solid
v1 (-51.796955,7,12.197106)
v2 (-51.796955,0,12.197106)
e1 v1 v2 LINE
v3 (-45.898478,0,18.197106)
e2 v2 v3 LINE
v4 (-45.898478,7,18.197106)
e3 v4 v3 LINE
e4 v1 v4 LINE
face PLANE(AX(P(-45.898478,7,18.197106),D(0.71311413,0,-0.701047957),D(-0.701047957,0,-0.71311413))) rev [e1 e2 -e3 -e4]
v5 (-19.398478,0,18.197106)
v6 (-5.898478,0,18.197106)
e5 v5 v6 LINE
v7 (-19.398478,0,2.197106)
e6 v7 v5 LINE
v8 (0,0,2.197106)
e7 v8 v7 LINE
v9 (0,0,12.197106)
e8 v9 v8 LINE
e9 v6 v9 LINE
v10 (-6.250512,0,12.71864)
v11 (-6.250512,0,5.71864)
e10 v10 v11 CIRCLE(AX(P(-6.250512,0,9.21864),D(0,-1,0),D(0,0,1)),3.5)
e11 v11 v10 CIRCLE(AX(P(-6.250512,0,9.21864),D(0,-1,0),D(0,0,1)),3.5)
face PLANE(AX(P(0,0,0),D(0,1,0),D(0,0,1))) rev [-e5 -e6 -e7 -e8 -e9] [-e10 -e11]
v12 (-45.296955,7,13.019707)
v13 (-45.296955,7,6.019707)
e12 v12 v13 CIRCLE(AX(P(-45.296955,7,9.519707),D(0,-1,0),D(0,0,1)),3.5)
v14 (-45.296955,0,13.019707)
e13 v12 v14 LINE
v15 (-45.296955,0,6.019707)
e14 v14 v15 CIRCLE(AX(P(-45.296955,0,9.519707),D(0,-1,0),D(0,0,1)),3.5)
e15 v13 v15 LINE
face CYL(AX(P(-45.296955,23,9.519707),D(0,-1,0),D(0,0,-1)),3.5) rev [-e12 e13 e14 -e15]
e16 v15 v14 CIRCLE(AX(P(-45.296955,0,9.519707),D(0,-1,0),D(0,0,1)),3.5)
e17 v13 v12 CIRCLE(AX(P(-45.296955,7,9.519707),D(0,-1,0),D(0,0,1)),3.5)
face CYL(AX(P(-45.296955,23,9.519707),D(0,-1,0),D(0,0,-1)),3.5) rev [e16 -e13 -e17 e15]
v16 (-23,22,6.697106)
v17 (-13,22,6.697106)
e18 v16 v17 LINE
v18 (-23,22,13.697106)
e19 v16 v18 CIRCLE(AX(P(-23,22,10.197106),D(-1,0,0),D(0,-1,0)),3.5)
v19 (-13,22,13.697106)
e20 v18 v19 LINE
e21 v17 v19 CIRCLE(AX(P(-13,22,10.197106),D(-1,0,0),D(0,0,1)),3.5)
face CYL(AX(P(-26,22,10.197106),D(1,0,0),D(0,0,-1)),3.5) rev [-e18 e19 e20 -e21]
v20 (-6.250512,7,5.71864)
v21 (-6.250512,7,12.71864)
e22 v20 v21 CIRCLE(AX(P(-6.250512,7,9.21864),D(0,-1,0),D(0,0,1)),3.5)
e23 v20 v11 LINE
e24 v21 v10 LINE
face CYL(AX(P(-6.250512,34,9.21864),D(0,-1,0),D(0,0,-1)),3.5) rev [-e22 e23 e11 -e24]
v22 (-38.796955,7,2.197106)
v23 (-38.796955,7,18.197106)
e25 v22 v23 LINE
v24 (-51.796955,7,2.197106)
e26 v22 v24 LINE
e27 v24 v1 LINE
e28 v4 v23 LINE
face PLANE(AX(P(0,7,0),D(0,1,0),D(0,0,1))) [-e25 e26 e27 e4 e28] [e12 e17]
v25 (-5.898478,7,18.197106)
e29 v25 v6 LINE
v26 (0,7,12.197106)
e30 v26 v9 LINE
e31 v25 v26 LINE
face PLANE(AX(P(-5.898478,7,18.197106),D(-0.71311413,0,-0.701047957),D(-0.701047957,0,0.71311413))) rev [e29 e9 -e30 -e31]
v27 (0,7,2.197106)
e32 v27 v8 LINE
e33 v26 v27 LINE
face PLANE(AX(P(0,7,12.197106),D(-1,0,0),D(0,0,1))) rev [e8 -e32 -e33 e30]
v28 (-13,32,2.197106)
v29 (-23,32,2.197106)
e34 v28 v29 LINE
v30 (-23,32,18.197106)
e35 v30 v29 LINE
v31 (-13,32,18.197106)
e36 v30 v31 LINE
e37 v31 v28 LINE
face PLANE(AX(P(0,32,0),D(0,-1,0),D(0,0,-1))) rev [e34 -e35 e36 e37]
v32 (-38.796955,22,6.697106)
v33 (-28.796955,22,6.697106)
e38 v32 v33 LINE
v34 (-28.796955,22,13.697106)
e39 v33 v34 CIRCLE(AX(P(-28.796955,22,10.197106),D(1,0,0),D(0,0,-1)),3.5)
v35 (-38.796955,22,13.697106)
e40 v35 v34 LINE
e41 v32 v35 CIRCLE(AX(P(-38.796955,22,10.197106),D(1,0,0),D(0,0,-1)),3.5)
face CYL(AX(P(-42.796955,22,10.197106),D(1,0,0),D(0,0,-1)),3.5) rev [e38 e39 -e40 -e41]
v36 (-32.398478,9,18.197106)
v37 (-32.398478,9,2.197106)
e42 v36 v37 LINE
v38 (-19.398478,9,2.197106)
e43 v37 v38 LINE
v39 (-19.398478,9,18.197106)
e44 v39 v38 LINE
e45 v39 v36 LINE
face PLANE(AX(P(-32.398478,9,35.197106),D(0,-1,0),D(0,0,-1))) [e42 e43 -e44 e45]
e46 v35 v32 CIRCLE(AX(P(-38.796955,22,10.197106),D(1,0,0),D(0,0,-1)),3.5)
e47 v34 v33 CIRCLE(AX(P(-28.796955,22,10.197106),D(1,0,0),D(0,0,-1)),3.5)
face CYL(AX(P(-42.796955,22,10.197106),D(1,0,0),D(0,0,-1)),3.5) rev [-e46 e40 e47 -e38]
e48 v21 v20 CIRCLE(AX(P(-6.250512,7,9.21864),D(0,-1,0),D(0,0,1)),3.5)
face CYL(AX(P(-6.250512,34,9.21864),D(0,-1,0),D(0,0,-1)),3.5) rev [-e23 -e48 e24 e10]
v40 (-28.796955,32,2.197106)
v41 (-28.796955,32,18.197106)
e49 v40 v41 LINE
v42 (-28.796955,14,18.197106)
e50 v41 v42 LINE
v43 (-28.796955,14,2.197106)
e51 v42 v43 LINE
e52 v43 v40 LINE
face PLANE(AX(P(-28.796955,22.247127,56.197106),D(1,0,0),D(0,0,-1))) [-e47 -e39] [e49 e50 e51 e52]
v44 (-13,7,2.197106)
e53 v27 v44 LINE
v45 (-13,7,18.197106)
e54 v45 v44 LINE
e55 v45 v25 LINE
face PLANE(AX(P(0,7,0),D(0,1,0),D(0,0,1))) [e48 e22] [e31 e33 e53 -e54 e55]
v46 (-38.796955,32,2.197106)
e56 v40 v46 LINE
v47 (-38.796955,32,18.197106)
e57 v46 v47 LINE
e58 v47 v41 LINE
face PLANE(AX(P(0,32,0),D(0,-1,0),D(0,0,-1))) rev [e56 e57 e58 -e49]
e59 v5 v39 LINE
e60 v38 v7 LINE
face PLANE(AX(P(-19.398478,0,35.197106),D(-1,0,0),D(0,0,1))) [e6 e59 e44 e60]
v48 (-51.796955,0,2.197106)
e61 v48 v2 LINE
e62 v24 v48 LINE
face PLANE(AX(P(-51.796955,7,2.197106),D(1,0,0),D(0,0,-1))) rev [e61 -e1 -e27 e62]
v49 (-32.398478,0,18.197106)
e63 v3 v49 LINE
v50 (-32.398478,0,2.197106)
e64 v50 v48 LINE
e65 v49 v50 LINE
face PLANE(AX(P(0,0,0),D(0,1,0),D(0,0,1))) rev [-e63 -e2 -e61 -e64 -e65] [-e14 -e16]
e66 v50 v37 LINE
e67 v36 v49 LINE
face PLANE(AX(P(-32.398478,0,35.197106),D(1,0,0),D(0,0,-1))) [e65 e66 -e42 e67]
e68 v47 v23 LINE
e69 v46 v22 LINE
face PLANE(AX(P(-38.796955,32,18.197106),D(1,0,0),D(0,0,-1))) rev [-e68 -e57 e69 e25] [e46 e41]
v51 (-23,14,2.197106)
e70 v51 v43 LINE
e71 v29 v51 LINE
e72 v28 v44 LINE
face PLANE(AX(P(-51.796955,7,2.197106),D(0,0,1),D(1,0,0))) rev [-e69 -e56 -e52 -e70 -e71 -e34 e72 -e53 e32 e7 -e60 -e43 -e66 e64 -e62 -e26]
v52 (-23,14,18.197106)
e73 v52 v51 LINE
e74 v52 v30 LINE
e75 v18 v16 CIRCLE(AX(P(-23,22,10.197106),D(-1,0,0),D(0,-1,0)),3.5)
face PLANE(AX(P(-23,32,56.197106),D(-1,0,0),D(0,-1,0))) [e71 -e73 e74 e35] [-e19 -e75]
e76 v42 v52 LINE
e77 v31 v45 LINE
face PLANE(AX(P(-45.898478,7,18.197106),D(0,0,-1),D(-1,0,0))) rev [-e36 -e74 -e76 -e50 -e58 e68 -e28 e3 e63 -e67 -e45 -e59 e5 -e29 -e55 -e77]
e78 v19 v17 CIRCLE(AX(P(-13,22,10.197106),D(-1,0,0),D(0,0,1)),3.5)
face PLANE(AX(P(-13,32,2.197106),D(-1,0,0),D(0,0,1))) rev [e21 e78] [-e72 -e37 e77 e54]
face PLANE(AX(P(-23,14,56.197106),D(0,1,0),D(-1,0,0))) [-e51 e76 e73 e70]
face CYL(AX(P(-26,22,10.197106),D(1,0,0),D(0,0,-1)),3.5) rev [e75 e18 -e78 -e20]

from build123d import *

# Parameters (mm, degrees)
BASE_PLATE_DEPTH              = 7
BASE_RELIEF_CUT_DEPTH         = 16
BASE_RELIEF_CUT_DEPTH_BACK    = 18
BASE_RELIEF_CUT_SKETCH_R      = 3.5
BASE_TRIM_CUT_DEPTH           = 27
BASE_TRIM_CUT_DEPTH_BACK      = 35
BASE_TRIM_CUT_SKETCH_R        = 3.5
UPRIGHT_BLOCK_SKETCH_13X13_W  = 25.796955258
UPRIGHT_BLOCK_SKETCH_13X13_H  = 16
UPRIGHT_BLOCK_DEPTH           = 25
UPRIGHT_SLOT_DEPTH            = 38
UPRIGHT_SLOT_DEPTH_BACK       = 84
UPRIGHT_CROSS_HOLE_DEPTH      = 10
UPRIGHT_CROSS_HOLE_DEPTH_BACK = 13
UPRIGHT_CROSS_HOLE_SKETCH_R   = 3.5
THROUGH_HOLE_SKETCH_R         = 3.5
THROUGH_HOLE_DEPTH            = 14
BASE_CLEARANCE_CUT_DEPTH      = 17
BASE_CLEARANCE_CUT_DEPTH_BACK = 58
BASE_CLEARANCE_CUT_SKETCH_W   = 13
BASE_CLEARANCE_CUT_SKETCH_H   = 9


with BuildPart() as part:
    # Base Plate Sketch → Base Plate (new body)
    with BuildSketch(Plane(origin=(0, 0, 0), x_dir=(1, 0, 0), z_dir=(0, 1, 0))):
        Polygon((-51.796955258, -2.197106083), (-51.796955258, -12.197106083), (-45.898477629, -18.197106083), (-5.898477629, -18.197106083), (0, -12.197106083), (0, -2.197106083), align=None)
    extrude(amount=BASE_PLATE_DEPTH)

    # Base Relief Cut Sketch → Base Relief Cut (cut, two sides: drawn at the far end of the back side and taken through both)
    with BuildSketch(Plane(origin=(0, 7, 0), x_dir=(1, 0, 0), z_dir=(0, 1, 0)).offset(-BASE_RELIEF_CUT_DEPTH_BACK)):
        with Locations(Location((-45.296955258, -9.519706742, 0), (0, 0, 270))):
            Circle(BASE_RELIEF_CUT_SKETCH_R)
    extrude(amount=BASE_RELIEF_CUT_DEPTH + BASE_RELIEF_CUT_DEPTH_BACK, mode=Mode.SUBTRACT)

    # Base Trim Cut Sketch → Base Trim Cut (cut, two sides: drawn at the far end of the back side and taken through both)
    with BuildSketch(Plane(origin=(0, 7, 0), x_dir=(1, 0, 0), z_dir=(0, 1, 0)).offset(-BASE_TRIM_CUT_DEPTH_BACK)):
        with Locations(Location((-6.250512003, -9.218640368, 0), (0, 0, 270))):
            Circle(BASE_TRIM_CUT_SKETCH_R)
    extrude(amount=BASE_TRIM_CUT_DEPTH + BASE_TRIM_CUT_DEPTH_BACK, mode=Mode.SUBTRACT)

    # Upright Block Sketch 13x13 → Upright Block (add)
    with BuildSketch(Plane(origin=(0, 7, 0), x_dir=(1, 0, 0), z_dir=(0, 1, 0))):
        with Locations((-25.898477629, -10.197106083)):
            Rectangle(UPRIGHT_BLOCK_SKETCH_13X13_W, UPRIGHT_BLOCK_SKETCH_13X13_H)
    extrude(amount=UPRIGHT_BLOCK_DEPTH)

    # Upright Slot Sketch → Upright Slot (cut, two sides: drawn at the far end of the back side and taken through both)
    with BuildSketch(Plane.XY.offset(18.197106083).offset(-UPRIGHT_SLOT_DEPTH_BACK)):
        Polygon((-28.796955258, 32), (-28.796955258, 22.247127252), (-28.796955258, 14), (-23, 14), (-23, 32), align=None)
    extrude(amount=UPRIGHT_SLOT_DEPTH + UPRIGHT_SLOT_DEPTH_BACK, mode=Mode.SUBTRACT)

    # Upright Cross Hole Sketch → Upright Cross Hole (cut, two sides: drawn at the far end of the back side and taken through both)
    with BuildSketch(Plane(origin=(-13, 0, 0), x_dir=(0, 0, -1), z_dir=(1, 0, 0)).offset(-UPRIGHT_CROSS_HOLE_DEPTH_BACK)):
        with Locations(Location((-10.197106083, 22, 0), (0, 0, 270))):
            Circle(UPRIGHT_CROSS_HOLE_SKETCH_R)
    extrude(amount=UPRIGHT_CROSS_HOLE_DEPTH + UPRIGHT_CROSS_HOLE_DEPTH_BACK, mode=Mode.SUBTRACT)

    # Through Hole Sketch → Through Hole (cut)
    with BuildSketch(Plane(origin=(-28.796955258, 0, 0), x_dir=(0, 0, -1), z_dir=(1, 0, 0))):
        with Locations(Location((-10.197106083, 22, 0), (0, 0, 270))):
            Circle(THROUGH_HOLE_SKETCH_R)
    extrude(amount=-THROUGH_HOLE_DEPTH, mode=Mode.SUBTRACT)

    # Base Clearance Cut Sketch → Base Clearance Cut (cut, two sides: drawn at the far end of the back side and taken through both)
    with BuildSketch(Plane.XY.offset(18.197106083).offset(-BASE_CLEARANCE_CUT_DEPTH_BACK)):
        with Locations((-25.898477629, 4.5)):
            Rectangle(BASE_CLEARANCE_CUT_SKETCH_W, BASE_CLEARANCE_CUT_SKETCH_H)
    extrude(amount=BASE_CLEARANCE_CUT_DEPTH + BASE_CLEARANCE_CUT_DEPTH_BACK, mode=Mode.SUBTRACT)


solid = part.part
